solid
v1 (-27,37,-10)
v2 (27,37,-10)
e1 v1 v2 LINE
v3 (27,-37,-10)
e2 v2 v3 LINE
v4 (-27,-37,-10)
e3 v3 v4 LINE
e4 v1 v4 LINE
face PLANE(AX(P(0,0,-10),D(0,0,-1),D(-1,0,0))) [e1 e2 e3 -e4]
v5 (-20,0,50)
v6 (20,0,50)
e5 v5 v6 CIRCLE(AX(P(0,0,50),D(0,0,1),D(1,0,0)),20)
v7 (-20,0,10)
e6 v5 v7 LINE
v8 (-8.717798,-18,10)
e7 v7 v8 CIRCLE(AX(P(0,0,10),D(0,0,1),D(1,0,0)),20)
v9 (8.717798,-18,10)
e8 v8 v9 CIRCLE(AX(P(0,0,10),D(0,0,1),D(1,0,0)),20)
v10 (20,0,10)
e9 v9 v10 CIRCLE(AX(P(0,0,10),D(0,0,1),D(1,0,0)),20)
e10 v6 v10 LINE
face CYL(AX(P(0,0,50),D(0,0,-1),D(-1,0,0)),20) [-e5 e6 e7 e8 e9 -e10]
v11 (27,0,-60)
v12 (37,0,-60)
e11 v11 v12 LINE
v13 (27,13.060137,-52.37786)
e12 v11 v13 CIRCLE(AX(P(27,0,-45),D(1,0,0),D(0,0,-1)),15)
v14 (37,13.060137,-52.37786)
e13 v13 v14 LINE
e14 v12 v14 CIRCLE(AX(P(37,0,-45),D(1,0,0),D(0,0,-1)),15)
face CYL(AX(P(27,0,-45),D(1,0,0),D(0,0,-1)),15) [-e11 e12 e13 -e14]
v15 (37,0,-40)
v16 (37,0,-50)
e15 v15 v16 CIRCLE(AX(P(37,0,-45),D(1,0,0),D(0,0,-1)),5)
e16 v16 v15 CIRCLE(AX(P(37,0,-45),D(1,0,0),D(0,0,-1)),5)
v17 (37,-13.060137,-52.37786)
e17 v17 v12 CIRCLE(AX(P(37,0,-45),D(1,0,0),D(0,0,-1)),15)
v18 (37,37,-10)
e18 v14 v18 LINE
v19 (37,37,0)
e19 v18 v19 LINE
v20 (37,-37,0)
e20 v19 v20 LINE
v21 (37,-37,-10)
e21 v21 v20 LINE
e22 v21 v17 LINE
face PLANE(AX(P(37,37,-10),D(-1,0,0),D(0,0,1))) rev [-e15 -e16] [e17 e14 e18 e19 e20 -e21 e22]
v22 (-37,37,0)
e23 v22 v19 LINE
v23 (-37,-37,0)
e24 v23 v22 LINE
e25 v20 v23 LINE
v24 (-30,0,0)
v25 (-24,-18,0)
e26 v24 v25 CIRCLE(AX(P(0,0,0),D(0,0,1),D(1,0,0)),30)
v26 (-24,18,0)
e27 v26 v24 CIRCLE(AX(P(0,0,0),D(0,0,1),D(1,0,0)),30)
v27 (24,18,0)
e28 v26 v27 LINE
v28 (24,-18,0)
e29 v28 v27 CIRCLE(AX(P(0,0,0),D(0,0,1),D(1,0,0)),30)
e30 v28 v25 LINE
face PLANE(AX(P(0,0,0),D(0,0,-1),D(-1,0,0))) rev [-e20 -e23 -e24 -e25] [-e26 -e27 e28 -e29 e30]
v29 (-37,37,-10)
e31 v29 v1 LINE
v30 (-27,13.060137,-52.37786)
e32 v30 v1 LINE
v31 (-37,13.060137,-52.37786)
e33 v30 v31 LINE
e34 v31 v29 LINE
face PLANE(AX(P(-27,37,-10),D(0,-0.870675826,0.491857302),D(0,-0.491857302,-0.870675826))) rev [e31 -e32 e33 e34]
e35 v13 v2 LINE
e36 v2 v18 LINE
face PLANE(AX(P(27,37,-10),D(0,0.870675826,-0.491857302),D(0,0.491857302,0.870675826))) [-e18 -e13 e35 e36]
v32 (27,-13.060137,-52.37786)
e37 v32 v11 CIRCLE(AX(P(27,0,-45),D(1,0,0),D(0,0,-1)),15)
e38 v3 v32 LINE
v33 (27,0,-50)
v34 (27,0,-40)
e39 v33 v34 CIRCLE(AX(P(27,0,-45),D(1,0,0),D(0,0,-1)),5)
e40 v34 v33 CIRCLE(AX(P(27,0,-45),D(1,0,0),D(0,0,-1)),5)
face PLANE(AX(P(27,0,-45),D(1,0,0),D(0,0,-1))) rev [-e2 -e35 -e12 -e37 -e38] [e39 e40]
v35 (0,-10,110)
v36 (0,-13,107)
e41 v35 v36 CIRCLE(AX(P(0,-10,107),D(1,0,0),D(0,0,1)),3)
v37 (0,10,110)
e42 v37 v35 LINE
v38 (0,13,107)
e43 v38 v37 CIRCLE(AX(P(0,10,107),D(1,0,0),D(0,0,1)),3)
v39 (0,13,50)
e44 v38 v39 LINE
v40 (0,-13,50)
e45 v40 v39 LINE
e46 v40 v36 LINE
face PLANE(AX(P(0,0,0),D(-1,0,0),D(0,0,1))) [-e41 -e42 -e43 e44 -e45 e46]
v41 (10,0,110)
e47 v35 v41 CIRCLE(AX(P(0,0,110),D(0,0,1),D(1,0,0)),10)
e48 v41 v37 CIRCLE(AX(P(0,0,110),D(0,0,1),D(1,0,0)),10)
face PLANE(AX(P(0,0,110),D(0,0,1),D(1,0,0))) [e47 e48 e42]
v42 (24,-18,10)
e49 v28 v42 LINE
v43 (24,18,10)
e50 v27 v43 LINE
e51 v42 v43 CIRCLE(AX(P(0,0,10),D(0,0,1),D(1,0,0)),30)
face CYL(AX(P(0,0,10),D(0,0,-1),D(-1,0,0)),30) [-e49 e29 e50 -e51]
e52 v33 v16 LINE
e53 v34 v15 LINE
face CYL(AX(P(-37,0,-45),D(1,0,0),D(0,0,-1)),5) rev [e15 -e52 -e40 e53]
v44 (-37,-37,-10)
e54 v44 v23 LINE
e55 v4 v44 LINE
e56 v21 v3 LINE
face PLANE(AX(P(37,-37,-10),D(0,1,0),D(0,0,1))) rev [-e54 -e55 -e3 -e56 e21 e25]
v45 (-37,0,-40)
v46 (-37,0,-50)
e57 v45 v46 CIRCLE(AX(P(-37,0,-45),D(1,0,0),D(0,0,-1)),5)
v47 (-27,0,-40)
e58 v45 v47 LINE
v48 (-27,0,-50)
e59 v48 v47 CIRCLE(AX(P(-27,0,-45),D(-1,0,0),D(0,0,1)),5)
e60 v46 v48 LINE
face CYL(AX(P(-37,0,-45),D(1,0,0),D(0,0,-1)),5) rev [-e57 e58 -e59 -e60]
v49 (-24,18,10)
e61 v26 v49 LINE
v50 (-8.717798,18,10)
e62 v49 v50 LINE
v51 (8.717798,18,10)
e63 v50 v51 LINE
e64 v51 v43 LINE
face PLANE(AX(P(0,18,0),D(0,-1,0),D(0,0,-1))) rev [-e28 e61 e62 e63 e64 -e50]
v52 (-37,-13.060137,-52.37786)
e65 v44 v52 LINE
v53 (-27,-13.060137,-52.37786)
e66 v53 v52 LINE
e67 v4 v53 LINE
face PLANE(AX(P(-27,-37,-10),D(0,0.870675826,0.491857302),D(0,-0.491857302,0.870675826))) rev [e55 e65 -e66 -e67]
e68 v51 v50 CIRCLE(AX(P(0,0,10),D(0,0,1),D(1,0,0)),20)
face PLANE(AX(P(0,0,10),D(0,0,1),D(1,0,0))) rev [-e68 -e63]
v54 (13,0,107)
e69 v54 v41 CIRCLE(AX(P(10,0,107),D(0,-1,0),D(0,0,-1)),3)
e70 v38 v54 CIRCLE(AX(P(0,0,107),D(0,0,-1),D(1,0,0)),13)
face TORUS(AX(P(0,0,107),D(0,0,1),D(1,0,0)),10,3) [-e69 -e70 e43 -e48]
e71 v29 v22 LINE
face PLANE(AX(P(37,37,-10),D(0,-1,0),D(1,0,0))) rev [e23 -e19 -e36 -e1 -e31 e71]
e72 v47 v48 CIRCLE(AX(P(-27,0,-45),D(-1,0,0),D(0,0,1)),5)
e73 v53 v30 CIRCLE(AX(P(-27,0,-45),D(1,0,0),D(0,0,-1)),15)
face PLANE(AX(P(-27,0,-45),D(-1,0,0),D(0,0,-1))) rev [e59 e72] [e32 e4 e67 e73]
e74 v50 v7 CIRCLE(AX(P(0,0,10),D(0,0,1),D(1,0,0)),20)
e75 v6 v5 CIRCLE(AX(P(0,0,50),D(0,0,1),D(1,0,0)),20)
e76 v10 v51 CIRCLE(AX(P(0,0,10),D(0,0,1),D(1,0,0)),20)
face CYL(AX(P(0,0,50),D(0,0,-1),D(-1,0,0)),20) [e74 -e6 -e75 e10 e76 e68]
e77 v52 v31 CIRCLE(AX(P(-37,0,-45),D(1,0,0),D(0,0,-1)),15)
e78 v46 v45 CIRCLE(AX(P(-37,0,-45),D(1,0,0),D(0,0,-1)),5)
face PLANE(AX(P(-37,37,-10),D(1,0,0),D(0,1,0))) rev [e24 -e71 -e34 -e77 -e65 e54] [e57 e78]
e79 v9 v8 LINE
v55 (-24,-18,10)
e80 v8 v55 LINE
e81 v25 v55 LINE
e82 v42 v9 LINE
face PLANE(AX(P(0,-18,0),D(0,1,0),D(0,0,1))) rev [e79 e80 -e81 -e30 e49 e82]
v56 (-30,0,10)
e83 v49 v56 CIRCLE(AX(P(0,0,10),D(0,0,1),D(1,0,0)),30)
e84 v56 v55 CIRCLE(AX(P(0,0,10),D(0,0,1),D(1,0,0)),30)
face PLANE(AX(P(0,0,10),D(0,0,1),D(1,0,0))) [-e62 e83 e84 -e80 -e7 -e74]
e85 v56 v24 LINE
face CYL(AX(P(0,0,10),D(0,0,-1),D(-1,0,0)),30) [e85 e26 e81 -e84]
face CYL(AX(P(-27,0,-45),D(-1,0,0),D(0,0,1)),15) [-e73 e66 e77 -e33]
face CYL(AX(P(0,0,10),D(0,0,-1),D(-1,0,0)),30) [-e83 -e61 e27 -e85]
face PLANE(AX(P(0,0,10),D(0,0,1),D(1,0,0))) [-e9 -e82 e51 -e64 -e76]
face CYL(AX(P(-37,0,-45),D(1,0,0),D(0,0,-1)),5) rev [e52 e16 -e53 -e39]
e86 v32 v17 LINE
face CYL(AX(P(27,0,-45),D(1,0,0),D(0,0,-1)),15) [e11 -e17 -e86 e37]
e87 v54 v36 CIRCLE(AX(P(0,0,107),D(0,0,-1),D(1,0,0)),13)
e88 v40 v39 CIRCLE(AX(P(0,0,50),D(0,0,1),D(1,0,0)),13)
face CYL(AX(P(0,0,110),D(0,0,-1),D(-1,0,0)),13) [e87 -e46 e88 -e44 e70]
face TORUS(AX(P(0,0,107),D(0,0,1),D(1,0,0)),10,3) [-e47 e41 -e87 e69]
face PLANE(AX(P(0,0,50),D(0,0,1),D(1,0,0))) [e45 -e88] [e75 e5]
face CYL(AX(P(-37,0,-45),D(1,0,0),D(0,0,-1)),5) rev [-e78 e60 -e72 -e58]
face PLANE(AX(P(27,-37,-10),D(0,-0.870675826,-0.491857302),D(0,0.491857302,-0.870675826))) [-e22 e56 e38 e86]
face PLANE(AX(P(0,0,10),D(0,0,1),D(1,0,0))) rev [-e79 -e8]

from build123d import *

# Parameters (mm, degrees)
BASE_DISC_SKETCH_60_R       = 30
BASE_DISC_60_DEPTH          = 10
BASE_START                  = -10
BASE_PROFILE_CUT_DEPTH      = 10
COLLAR_SKETCH_40_R          = 20
COLLAR_40_DEPTH             = 40
SHAFT_SKETCH_26_R           = 13
SHAFT_26_DEPTH              = 60
SHAFT_END_FILLET_R3_R       = 3
SHAFT_FLAT_CUT_DEPTH        = 30
MOUNTING_FLANGE_SKETCH_74_W = 74
MOUNTING_FLANGE_SKETCH_74_H = 74
MOUNTING_FLANGE_74_DEPTH    = 10
MOUNTING_EAR_DEPTH          = 10
EAR_HOLE_SKETCH_10_R        = 5
EAR_HOLE_10_DEPTH           = 138.640836963


with BuildPart() as part:
    # Base Disc Sketch Ø60 → Base Disc Ø60 (new body)
    with BuildSketch(Plane.XY):
        Circle(BASE_DISC_SKETCH_60_R)
    extrude(amount=BASE_DISC_60_DEPTH)

    # Base Profile Cut Sketch → Base Profile Cut (cut)
    with BuildSketch(Plane.XY.offset(10).offset(BASE_START)):
        with BuildLine():
            Line((0, 18), (-24, 18))
            ThreePointArc((-24, 18), (0, 30), (24, 18))
            Line((24, 18), (0, 18))
        make_face()
        with BuildLine():
            Line((0, -18), (24, -18))
            ThreePointArc((24, -18), (0, -30), (-24, -18))
            Line((-24, -18), (0, -18))
        make_face()
    extrude(amount=BASE_PROFILE_CUT_DEPTH, mode=Mode.SUBTRACT)

    # Collar Sketch Ø40 → Collar Ø40 (add)
    with BuildSketch(Plane.XY.offset(10)):
        with Locations(Location((0, 0, 0), (0, 0, 115.841932763))):
            Circle(COLLAR_SKETCH_40_R)
    extrude(amount=COLLAR_40_DEPTH)

    # Shaft Sketch Ø26 → Shaft Ø26 (add)
    with BuildSketch(Plane.XY.offset(50)):
        Circle(SHAFT_SKETCH_26_R)
    extrude(amount=SHAFT_26_DEPTH)

    # Shaft End Fillet R3
    shaft_end_fillet_r3_edges = [part.edges().sort_by_distance(p)[0] for p in [
        (-13, 0, 110),
    ]]
    fillet(shaft_end_fillet_r3_edges, radius=SHAFT_END_FILLET_R3_R)

    # Shaft Flat Sketch → Shaft Flat Cut (cut)
    with BuildSketch(Plane(origin=(0, 0, 0), x_dir=(0, 0, -1), z_dir=(1, 0, 0))):
        Polygon((-107, 20.022291402), (-120.828706591, 20.022291402), (-120.828706591, -20.022291402), (-107, -20.022291402), (-50, -20.022291402), (-50, 20.022291402), align=None)
    extrude(amount=-SHAFT_FLAT_CUT_DEPTH, mode=Mode.SUBTRACT)

    # Mounting Flange Sketch 74 → Mounting Flange 74 (add)
    with BuildSketch(Plane(origin=(0, 0, 0), x_dir=(-1, 0, 0), z_dir=(0, 0, -1))):
        Rectangle(MOUNTING_FLANGE_SKETCH_74_W, MOUNTING_FLANGE_SKETCH_74_H)
    extrude(amount=MOUNTING_FLANGE_74_DEPTH)

    # Mounting Ear Sketch → Mounting Ear (add)
    with BuildSketch(Plane(origin=(37, 0, 0), x_dir=(0, 0, -1), z_dir=(1, 0, 0))):
        with BuildLine():
            Line((10, 37), (52.377859531, 13.060137394))
            ThreePointArc((52.377859531, 13.060137394), (60, 0), (52.377859531, -13.060137394))
            Line((52.377859531, -13.060137394), (10, -37))
            Line((10, -37), (10, 37))
        make_face()
    mounting_ear = extrude(amount=-MOUNTING_EAR_DEPTH)

    # Mounting Ear Mirror: Mounting Ear across plane
    add(mounting_ear.mirror(Plane(origin=(0, 0, 0), x_dir=(0, 0, 1), z_dir=(1, 0, 0))))

    # Ear Hole Sketch Ø10 → Ear Hole Ø10 (cut, through all)
    with BuildSketch(Plane(origin=(37, 0, 0), x_dir=(0, 0, -1), z_dir=(1, 0, 0))):
        with Locations((45, 0)):
            Circle(EAR_HOLE_SKETCH_10_R)
    extrude(amount=-EAR_HOLE_10_DEPTH, mode=Mode.SUBTRACT)


solid = part.part
